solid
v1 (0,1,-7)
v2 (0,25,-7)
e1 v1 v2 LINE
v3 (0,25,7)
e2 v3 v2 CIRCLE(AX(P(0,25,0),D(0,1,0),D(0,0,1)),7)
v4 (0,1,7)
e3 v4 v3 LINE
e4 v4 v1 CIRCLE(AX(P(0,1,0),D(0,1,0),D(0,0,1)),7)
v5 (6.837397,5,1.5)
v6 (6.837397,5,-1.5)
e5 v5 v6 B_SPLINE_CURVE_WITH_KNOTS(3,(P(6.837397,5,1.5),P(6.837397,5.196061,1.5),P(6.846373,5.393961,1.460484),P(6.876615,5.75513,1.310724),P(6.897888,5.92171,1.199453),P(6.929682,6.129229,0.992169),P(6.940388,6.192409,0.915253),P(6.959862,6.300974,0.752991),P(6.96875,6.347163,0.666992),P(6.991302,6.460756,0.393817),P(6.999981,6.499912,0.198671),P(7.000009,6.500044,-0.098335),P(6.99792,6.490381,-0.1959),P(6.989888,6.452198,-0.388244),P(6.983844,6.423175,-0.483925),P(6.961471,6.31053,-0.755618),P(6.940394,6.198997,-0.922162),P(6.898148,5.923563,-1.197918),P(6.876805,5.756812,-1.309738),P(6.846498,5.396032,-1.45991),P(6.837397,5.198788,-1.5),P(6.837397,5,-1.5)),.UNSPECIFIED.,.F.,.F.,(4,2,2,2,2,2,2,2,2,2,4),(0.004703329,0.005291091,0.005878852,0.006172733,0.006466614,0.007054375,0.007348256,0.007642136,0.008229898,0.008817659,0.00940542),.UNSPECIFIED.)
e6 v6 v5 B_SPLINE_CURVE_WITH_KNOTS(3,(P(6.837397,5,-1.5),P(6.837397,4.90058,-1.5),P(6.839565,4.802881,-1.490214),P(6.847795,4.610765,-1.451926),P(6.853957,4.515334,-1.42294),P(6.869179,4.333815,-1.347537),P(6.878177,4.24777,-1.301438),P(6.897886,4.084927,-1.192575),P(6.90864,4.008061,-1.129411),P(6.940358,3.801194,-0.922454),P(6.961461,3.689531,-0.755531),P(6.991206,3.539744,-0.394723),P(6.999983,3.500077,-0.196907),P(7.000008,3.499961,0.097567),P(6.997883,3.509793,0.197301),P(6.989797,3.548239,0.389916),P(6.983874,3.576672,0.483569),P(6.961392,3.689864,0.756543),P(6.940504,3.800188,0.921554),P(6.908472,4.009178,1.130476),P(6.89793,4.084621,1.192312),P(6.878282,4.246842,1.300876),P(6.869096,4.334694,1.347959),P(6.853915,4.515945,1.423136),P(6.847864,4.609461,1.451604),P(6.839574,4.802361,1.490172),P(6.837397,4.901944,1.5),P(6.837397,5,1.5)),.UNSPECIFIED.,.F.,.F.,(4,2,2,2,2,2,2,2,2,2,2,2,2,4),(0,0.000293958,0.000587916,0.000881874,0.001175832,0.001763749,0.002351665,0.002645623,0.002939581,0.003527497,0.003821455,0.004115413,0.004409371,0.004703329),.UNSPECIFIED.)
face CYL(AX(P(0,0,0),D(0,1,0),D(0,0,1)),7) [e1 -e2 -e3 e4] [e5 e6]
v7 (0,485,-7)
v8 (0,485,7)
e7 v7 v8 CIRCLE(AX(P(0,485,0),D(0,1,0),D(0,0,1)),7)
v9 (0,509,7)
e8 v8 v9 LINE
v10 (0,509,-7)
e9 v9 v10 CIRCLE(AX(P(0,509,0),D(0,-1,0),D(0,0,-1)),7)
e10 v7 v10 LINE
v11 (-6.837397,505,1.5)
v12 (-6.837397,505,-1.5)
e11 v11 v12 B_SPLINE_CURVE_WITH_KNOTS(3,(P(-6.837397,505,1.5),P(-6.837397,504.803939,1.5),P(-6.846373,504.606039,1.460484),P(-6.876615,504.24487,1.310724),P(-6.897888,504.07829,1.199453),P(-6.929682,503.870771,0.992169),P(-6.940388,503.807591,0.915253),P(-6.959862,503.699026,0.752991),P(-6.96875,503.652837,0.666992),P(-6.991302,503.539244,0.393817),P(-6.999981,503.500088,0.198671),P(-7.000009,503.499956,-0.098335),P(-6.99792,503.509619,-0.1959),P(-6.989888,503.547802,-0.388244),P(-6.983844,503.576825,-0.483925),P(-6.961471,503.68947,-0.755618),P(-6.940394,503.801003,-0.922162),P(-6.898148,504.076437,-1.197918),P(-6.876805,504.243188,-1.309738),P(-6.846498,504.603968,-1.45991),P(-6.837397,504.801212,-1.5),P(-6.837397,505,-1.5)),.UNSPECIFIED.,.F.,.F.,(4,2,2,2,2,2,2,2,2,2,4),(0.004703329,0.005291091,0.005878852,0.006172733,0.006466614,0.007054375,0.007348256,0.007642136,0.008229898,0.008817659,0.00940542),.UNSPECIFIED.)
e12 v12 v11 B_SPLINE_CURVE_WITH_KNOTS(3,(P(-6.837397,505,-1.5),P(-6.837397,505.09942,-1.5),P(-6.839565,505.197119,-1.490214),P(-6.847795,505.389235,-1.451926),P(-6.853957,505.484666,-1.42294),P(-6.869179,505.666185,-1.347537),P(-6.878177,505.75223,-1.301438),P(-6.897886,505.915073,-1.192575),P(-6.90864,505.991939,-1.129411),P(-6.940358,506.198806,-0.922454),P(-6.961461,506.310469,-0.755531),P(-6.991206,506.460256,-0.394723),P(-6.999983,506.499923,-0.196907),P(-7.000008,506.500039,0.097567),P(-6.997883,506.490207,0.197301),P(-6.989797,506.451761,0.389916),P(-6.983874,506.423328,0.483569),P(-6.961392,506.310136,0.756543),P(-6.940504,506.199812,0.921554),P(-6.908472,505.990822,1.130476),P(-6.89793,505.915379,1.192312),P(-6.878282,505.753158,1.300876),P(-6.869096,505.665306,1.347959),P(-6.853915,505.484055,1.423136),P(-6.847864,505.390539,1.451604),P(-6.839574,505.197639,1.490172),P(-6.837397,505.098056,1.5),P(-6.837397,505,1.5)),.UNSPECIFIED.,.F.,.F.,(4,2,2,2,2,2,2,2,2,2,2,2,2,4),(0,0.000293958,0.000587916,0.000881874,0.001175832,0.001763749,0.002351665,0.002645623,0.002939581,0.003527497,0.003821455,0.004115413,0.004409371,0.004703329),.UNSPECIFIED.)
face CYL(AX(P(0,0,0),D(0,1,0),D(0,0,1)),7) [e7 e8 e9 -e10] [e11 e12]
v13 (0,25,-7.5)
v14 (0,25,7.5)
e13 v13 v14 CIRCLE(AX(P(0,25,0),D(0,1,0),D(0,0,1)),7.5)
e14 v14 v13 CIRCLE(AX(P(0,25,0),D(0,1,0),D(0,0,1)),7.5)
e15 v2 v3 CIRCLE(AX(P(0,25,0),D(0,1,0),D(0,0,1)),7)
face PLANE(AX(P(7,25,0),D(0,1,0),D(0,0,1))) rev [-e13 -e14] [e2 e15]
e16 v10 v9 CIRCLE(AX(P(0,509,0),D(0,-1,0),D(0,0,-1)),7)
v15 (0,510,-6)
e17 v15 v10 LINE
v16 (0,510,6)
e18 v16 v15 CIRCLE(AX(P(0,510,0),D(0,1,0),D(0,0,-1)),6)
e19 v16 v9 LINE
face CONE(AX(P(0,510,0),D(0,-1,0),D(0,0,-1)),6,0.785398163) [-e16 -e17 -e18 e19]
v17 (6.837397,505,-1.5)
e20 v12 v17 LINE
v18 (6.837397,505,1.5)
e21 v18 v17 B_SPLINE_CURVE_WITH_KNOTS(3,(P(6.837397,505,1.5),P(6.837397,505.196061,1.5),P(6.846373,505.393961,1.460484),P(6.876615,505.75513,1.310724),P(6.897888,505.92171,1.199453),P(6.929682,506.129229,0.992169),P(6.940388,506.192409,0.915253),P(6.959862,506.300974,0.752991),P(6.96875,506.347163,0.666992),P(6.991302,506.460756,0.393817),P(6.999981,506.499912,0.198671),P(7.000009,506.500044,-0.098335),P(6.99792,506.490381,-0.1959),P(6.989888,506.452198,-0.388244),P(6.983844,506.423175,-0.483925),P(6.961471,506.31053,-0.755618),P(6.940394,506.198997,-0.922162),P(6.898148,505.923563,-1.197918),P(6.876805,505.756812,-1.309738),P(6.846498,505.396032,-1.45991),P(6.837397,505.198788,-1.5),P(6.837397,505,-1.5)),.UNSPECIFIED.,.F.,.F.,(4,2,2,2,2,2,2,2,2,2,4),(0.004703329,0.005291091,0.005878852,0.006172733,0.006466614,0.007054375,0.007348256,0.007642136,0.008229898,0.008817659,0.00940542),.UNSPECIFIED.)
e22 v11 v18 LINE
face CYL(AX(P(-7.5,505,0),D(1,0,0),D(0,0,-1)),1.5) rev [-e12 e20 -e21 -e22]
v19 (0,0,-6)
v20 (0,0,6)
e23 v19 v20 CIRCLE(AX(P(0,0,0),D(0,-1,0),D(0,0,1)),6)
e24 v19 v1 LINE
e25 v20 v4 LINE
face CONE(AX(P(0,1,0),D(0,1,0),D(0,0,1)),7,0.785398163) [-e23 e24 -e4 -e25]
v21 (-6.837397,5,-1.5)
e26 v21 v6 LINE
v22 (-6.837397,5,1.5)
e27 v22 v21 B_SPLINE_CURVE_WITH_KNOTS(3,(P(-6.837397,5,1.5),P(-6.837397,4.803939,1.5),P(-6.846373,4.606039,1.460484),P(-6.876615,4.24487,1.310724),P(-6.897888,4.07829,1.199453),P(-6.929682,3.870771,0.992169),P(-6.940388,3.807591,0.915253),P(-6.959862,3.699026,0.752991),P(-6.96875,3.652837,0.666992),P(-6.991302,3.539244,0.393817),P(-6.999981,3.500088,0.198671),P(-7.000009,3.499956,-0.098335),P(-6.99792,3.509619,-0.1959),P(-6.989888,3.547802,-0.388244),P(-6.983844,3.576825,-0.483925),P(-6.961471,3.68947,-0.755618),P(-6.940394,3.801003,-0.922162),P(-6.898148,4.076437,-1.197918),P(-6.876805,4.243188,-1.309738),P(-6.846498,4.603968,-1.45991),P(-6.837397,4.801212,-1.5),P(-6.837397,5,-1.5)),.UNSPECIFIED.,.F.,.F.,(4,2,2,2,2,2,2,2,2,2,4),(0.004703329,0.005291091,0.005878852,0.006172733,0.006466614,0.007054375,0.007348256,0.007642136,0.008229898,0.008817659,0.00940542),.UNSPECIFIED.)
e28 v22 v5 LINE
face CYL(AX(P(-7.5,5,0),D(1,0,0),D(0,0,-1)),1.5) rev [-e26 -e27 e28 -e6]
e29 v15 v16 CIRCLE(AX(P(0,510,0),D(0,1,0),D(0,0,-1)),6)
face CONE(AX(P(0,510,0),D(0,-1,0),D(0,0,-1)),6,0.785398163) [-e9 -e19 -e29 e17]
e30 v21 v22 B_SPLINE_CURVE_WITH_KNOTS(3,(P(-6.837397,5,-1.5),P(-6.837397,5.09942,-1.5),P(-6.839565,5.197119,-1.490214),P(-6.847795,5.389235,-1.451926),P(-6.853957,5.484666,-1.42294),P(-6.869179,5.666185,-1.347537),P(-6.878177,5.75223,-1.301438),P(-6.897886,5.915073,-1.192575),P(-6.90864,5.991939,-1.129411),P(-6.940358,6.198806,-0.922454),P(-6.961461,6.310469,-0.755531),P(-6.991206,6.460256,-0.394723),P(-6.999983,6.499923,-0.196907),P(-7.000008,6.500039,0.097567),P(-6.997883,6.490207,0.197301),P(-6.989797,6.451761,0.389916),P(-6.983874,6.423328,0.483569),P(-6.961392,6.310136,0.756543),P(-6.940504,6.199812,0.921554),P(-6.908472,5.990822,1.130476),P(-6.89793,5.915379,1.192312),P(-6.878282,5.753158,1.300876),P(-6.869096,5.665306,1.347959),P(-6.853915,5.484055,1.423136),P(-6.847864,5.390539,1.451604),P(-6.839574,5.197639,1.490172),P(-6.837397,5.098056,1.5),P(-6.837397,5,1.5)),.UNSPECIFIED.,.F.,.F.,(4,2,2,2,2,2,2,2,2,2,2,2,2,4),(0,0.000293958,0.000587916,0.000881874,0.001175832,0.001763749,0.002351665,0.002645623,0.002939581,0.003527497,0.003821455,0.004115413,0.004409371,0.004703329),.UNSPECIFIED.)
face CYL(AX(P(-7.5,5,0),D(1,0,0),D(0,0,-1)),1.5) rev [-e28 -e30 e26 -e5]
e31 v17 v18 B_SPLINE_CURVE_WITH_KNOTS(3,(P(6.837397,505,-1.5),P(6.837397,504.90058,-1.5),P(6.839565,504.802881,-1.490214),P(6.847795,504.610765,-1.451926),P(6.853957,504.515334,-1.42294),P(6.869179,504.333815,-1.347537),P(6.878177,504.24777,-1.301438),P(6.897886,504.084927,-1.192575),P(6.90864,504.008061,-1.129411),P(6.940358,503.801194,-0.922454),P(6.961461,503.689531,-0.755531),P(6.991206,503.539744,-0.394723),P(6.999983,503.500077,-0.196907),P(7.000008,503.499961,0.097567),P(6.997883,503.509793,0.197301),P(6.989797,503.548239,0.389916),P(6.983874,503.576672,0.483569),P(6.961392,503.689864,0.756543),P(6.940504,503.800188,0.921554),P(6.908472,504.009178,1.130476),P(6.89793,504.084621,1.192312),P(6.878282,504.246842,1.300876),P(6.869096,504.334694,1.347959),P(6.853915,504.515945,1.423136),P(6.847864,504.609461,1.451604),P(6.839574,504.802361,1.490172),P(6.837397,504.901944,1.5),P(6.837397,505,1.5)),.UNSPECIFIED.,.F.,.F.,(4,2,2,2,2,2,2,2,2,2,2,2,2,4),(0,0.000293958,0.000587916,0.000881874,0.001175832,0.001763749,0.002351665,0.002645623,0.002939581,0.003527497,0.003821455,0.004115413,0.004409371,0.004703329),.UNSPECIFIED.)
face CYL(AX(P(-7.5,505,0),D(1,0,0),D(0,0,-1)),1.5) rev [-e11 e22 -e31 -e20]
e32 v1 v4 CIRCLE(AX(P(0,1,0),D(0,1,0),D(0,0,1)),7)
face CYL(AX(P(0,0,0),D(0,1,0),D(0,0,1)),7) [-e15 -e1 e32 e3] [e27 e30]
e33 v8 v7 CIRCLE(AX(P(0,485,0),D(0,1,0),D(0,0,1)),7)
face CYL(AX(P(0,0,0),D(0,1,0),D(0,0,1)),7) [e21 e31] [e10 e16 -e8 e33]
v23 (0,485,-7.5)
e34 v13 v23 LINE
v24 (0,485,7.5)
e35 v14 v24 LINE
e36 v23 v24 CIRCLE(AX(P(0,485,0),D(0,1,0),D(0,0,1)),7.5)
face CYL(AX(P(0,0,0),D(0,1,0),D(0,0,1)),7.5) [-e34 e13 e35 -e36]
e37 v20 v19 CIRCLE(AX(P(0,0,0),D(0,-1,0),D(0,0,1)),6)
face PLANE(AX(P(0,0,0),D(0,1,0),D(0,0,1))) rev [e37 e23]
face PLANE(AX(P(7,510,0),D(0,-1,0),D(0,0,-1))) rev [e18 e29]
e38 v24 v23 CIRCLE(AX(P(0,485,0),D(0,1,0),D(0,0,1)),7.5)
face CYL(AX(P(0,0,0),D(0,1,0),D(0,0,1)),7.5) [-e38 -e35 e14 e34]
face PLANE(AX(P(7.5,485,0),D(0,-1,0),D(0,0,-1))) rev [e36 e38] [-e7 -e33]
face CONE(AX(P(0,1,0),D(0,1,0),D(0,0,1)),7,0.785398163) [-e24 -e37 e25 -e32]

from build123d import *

# Parameters (mm, degrees)
CHAMFER1_SIZE           = 1
CUT_EXTRUDE1_DEPTH      = 511.110282194
CUT_EXTRUDE1_DEPTH_BACK = 511.110282194
SKETCH3_R               = 1.5


with BuildPart() as part:
    # Sketch1 → Revolve1 (revolve)
    with BuildSketch(Plane.XY, mode=Mode.PRIVATE) as revolve1_sk:
        Polygon((0, 0), (7, 0), (7, 25), (7.5, 25), (7.5, 485), (7, 485), (7, 510), (0, 510), align=None)
    revolve(revolve1_sk.sketch.rotate(Axis((0, 0, 0), (0, -1, 0)), 90), axis=Axis((0, 0, 0), (0, -1, 0)))

    # Chamfer1
    chamfer1_edges = [part.edges().sort_by_distance(p)[0] for p in [
        (0, 510, -7),
        (0, 0, -7),
    ]]
    chamfer(chamfer1_edges, length=CHAMFER1_SIZE)

    # Sketch3 → Cut-Extrude1 (cut, two sides: drawn at the far end of the back side and taken through both)
    with BuildSketch(Plane(origin=(0, 0, 0), x_dir=(0, 0, -1), z_dir=(1, 0, 0)).offset(-CUT_EXTRUDE1_DEPTH_BACK)):
        with Locations((0, 505)):
            Circle(SKETCH3_R)
        with Locations((0, 5)):
            Circle(SKETCH3_R)
    extrude(amount=CUT_EXTRUDE1_DEPTH + CUT_EXTRUDE1_DEPTH_BACK, mode=Mode.SUBTRACT)


solid = part.part
